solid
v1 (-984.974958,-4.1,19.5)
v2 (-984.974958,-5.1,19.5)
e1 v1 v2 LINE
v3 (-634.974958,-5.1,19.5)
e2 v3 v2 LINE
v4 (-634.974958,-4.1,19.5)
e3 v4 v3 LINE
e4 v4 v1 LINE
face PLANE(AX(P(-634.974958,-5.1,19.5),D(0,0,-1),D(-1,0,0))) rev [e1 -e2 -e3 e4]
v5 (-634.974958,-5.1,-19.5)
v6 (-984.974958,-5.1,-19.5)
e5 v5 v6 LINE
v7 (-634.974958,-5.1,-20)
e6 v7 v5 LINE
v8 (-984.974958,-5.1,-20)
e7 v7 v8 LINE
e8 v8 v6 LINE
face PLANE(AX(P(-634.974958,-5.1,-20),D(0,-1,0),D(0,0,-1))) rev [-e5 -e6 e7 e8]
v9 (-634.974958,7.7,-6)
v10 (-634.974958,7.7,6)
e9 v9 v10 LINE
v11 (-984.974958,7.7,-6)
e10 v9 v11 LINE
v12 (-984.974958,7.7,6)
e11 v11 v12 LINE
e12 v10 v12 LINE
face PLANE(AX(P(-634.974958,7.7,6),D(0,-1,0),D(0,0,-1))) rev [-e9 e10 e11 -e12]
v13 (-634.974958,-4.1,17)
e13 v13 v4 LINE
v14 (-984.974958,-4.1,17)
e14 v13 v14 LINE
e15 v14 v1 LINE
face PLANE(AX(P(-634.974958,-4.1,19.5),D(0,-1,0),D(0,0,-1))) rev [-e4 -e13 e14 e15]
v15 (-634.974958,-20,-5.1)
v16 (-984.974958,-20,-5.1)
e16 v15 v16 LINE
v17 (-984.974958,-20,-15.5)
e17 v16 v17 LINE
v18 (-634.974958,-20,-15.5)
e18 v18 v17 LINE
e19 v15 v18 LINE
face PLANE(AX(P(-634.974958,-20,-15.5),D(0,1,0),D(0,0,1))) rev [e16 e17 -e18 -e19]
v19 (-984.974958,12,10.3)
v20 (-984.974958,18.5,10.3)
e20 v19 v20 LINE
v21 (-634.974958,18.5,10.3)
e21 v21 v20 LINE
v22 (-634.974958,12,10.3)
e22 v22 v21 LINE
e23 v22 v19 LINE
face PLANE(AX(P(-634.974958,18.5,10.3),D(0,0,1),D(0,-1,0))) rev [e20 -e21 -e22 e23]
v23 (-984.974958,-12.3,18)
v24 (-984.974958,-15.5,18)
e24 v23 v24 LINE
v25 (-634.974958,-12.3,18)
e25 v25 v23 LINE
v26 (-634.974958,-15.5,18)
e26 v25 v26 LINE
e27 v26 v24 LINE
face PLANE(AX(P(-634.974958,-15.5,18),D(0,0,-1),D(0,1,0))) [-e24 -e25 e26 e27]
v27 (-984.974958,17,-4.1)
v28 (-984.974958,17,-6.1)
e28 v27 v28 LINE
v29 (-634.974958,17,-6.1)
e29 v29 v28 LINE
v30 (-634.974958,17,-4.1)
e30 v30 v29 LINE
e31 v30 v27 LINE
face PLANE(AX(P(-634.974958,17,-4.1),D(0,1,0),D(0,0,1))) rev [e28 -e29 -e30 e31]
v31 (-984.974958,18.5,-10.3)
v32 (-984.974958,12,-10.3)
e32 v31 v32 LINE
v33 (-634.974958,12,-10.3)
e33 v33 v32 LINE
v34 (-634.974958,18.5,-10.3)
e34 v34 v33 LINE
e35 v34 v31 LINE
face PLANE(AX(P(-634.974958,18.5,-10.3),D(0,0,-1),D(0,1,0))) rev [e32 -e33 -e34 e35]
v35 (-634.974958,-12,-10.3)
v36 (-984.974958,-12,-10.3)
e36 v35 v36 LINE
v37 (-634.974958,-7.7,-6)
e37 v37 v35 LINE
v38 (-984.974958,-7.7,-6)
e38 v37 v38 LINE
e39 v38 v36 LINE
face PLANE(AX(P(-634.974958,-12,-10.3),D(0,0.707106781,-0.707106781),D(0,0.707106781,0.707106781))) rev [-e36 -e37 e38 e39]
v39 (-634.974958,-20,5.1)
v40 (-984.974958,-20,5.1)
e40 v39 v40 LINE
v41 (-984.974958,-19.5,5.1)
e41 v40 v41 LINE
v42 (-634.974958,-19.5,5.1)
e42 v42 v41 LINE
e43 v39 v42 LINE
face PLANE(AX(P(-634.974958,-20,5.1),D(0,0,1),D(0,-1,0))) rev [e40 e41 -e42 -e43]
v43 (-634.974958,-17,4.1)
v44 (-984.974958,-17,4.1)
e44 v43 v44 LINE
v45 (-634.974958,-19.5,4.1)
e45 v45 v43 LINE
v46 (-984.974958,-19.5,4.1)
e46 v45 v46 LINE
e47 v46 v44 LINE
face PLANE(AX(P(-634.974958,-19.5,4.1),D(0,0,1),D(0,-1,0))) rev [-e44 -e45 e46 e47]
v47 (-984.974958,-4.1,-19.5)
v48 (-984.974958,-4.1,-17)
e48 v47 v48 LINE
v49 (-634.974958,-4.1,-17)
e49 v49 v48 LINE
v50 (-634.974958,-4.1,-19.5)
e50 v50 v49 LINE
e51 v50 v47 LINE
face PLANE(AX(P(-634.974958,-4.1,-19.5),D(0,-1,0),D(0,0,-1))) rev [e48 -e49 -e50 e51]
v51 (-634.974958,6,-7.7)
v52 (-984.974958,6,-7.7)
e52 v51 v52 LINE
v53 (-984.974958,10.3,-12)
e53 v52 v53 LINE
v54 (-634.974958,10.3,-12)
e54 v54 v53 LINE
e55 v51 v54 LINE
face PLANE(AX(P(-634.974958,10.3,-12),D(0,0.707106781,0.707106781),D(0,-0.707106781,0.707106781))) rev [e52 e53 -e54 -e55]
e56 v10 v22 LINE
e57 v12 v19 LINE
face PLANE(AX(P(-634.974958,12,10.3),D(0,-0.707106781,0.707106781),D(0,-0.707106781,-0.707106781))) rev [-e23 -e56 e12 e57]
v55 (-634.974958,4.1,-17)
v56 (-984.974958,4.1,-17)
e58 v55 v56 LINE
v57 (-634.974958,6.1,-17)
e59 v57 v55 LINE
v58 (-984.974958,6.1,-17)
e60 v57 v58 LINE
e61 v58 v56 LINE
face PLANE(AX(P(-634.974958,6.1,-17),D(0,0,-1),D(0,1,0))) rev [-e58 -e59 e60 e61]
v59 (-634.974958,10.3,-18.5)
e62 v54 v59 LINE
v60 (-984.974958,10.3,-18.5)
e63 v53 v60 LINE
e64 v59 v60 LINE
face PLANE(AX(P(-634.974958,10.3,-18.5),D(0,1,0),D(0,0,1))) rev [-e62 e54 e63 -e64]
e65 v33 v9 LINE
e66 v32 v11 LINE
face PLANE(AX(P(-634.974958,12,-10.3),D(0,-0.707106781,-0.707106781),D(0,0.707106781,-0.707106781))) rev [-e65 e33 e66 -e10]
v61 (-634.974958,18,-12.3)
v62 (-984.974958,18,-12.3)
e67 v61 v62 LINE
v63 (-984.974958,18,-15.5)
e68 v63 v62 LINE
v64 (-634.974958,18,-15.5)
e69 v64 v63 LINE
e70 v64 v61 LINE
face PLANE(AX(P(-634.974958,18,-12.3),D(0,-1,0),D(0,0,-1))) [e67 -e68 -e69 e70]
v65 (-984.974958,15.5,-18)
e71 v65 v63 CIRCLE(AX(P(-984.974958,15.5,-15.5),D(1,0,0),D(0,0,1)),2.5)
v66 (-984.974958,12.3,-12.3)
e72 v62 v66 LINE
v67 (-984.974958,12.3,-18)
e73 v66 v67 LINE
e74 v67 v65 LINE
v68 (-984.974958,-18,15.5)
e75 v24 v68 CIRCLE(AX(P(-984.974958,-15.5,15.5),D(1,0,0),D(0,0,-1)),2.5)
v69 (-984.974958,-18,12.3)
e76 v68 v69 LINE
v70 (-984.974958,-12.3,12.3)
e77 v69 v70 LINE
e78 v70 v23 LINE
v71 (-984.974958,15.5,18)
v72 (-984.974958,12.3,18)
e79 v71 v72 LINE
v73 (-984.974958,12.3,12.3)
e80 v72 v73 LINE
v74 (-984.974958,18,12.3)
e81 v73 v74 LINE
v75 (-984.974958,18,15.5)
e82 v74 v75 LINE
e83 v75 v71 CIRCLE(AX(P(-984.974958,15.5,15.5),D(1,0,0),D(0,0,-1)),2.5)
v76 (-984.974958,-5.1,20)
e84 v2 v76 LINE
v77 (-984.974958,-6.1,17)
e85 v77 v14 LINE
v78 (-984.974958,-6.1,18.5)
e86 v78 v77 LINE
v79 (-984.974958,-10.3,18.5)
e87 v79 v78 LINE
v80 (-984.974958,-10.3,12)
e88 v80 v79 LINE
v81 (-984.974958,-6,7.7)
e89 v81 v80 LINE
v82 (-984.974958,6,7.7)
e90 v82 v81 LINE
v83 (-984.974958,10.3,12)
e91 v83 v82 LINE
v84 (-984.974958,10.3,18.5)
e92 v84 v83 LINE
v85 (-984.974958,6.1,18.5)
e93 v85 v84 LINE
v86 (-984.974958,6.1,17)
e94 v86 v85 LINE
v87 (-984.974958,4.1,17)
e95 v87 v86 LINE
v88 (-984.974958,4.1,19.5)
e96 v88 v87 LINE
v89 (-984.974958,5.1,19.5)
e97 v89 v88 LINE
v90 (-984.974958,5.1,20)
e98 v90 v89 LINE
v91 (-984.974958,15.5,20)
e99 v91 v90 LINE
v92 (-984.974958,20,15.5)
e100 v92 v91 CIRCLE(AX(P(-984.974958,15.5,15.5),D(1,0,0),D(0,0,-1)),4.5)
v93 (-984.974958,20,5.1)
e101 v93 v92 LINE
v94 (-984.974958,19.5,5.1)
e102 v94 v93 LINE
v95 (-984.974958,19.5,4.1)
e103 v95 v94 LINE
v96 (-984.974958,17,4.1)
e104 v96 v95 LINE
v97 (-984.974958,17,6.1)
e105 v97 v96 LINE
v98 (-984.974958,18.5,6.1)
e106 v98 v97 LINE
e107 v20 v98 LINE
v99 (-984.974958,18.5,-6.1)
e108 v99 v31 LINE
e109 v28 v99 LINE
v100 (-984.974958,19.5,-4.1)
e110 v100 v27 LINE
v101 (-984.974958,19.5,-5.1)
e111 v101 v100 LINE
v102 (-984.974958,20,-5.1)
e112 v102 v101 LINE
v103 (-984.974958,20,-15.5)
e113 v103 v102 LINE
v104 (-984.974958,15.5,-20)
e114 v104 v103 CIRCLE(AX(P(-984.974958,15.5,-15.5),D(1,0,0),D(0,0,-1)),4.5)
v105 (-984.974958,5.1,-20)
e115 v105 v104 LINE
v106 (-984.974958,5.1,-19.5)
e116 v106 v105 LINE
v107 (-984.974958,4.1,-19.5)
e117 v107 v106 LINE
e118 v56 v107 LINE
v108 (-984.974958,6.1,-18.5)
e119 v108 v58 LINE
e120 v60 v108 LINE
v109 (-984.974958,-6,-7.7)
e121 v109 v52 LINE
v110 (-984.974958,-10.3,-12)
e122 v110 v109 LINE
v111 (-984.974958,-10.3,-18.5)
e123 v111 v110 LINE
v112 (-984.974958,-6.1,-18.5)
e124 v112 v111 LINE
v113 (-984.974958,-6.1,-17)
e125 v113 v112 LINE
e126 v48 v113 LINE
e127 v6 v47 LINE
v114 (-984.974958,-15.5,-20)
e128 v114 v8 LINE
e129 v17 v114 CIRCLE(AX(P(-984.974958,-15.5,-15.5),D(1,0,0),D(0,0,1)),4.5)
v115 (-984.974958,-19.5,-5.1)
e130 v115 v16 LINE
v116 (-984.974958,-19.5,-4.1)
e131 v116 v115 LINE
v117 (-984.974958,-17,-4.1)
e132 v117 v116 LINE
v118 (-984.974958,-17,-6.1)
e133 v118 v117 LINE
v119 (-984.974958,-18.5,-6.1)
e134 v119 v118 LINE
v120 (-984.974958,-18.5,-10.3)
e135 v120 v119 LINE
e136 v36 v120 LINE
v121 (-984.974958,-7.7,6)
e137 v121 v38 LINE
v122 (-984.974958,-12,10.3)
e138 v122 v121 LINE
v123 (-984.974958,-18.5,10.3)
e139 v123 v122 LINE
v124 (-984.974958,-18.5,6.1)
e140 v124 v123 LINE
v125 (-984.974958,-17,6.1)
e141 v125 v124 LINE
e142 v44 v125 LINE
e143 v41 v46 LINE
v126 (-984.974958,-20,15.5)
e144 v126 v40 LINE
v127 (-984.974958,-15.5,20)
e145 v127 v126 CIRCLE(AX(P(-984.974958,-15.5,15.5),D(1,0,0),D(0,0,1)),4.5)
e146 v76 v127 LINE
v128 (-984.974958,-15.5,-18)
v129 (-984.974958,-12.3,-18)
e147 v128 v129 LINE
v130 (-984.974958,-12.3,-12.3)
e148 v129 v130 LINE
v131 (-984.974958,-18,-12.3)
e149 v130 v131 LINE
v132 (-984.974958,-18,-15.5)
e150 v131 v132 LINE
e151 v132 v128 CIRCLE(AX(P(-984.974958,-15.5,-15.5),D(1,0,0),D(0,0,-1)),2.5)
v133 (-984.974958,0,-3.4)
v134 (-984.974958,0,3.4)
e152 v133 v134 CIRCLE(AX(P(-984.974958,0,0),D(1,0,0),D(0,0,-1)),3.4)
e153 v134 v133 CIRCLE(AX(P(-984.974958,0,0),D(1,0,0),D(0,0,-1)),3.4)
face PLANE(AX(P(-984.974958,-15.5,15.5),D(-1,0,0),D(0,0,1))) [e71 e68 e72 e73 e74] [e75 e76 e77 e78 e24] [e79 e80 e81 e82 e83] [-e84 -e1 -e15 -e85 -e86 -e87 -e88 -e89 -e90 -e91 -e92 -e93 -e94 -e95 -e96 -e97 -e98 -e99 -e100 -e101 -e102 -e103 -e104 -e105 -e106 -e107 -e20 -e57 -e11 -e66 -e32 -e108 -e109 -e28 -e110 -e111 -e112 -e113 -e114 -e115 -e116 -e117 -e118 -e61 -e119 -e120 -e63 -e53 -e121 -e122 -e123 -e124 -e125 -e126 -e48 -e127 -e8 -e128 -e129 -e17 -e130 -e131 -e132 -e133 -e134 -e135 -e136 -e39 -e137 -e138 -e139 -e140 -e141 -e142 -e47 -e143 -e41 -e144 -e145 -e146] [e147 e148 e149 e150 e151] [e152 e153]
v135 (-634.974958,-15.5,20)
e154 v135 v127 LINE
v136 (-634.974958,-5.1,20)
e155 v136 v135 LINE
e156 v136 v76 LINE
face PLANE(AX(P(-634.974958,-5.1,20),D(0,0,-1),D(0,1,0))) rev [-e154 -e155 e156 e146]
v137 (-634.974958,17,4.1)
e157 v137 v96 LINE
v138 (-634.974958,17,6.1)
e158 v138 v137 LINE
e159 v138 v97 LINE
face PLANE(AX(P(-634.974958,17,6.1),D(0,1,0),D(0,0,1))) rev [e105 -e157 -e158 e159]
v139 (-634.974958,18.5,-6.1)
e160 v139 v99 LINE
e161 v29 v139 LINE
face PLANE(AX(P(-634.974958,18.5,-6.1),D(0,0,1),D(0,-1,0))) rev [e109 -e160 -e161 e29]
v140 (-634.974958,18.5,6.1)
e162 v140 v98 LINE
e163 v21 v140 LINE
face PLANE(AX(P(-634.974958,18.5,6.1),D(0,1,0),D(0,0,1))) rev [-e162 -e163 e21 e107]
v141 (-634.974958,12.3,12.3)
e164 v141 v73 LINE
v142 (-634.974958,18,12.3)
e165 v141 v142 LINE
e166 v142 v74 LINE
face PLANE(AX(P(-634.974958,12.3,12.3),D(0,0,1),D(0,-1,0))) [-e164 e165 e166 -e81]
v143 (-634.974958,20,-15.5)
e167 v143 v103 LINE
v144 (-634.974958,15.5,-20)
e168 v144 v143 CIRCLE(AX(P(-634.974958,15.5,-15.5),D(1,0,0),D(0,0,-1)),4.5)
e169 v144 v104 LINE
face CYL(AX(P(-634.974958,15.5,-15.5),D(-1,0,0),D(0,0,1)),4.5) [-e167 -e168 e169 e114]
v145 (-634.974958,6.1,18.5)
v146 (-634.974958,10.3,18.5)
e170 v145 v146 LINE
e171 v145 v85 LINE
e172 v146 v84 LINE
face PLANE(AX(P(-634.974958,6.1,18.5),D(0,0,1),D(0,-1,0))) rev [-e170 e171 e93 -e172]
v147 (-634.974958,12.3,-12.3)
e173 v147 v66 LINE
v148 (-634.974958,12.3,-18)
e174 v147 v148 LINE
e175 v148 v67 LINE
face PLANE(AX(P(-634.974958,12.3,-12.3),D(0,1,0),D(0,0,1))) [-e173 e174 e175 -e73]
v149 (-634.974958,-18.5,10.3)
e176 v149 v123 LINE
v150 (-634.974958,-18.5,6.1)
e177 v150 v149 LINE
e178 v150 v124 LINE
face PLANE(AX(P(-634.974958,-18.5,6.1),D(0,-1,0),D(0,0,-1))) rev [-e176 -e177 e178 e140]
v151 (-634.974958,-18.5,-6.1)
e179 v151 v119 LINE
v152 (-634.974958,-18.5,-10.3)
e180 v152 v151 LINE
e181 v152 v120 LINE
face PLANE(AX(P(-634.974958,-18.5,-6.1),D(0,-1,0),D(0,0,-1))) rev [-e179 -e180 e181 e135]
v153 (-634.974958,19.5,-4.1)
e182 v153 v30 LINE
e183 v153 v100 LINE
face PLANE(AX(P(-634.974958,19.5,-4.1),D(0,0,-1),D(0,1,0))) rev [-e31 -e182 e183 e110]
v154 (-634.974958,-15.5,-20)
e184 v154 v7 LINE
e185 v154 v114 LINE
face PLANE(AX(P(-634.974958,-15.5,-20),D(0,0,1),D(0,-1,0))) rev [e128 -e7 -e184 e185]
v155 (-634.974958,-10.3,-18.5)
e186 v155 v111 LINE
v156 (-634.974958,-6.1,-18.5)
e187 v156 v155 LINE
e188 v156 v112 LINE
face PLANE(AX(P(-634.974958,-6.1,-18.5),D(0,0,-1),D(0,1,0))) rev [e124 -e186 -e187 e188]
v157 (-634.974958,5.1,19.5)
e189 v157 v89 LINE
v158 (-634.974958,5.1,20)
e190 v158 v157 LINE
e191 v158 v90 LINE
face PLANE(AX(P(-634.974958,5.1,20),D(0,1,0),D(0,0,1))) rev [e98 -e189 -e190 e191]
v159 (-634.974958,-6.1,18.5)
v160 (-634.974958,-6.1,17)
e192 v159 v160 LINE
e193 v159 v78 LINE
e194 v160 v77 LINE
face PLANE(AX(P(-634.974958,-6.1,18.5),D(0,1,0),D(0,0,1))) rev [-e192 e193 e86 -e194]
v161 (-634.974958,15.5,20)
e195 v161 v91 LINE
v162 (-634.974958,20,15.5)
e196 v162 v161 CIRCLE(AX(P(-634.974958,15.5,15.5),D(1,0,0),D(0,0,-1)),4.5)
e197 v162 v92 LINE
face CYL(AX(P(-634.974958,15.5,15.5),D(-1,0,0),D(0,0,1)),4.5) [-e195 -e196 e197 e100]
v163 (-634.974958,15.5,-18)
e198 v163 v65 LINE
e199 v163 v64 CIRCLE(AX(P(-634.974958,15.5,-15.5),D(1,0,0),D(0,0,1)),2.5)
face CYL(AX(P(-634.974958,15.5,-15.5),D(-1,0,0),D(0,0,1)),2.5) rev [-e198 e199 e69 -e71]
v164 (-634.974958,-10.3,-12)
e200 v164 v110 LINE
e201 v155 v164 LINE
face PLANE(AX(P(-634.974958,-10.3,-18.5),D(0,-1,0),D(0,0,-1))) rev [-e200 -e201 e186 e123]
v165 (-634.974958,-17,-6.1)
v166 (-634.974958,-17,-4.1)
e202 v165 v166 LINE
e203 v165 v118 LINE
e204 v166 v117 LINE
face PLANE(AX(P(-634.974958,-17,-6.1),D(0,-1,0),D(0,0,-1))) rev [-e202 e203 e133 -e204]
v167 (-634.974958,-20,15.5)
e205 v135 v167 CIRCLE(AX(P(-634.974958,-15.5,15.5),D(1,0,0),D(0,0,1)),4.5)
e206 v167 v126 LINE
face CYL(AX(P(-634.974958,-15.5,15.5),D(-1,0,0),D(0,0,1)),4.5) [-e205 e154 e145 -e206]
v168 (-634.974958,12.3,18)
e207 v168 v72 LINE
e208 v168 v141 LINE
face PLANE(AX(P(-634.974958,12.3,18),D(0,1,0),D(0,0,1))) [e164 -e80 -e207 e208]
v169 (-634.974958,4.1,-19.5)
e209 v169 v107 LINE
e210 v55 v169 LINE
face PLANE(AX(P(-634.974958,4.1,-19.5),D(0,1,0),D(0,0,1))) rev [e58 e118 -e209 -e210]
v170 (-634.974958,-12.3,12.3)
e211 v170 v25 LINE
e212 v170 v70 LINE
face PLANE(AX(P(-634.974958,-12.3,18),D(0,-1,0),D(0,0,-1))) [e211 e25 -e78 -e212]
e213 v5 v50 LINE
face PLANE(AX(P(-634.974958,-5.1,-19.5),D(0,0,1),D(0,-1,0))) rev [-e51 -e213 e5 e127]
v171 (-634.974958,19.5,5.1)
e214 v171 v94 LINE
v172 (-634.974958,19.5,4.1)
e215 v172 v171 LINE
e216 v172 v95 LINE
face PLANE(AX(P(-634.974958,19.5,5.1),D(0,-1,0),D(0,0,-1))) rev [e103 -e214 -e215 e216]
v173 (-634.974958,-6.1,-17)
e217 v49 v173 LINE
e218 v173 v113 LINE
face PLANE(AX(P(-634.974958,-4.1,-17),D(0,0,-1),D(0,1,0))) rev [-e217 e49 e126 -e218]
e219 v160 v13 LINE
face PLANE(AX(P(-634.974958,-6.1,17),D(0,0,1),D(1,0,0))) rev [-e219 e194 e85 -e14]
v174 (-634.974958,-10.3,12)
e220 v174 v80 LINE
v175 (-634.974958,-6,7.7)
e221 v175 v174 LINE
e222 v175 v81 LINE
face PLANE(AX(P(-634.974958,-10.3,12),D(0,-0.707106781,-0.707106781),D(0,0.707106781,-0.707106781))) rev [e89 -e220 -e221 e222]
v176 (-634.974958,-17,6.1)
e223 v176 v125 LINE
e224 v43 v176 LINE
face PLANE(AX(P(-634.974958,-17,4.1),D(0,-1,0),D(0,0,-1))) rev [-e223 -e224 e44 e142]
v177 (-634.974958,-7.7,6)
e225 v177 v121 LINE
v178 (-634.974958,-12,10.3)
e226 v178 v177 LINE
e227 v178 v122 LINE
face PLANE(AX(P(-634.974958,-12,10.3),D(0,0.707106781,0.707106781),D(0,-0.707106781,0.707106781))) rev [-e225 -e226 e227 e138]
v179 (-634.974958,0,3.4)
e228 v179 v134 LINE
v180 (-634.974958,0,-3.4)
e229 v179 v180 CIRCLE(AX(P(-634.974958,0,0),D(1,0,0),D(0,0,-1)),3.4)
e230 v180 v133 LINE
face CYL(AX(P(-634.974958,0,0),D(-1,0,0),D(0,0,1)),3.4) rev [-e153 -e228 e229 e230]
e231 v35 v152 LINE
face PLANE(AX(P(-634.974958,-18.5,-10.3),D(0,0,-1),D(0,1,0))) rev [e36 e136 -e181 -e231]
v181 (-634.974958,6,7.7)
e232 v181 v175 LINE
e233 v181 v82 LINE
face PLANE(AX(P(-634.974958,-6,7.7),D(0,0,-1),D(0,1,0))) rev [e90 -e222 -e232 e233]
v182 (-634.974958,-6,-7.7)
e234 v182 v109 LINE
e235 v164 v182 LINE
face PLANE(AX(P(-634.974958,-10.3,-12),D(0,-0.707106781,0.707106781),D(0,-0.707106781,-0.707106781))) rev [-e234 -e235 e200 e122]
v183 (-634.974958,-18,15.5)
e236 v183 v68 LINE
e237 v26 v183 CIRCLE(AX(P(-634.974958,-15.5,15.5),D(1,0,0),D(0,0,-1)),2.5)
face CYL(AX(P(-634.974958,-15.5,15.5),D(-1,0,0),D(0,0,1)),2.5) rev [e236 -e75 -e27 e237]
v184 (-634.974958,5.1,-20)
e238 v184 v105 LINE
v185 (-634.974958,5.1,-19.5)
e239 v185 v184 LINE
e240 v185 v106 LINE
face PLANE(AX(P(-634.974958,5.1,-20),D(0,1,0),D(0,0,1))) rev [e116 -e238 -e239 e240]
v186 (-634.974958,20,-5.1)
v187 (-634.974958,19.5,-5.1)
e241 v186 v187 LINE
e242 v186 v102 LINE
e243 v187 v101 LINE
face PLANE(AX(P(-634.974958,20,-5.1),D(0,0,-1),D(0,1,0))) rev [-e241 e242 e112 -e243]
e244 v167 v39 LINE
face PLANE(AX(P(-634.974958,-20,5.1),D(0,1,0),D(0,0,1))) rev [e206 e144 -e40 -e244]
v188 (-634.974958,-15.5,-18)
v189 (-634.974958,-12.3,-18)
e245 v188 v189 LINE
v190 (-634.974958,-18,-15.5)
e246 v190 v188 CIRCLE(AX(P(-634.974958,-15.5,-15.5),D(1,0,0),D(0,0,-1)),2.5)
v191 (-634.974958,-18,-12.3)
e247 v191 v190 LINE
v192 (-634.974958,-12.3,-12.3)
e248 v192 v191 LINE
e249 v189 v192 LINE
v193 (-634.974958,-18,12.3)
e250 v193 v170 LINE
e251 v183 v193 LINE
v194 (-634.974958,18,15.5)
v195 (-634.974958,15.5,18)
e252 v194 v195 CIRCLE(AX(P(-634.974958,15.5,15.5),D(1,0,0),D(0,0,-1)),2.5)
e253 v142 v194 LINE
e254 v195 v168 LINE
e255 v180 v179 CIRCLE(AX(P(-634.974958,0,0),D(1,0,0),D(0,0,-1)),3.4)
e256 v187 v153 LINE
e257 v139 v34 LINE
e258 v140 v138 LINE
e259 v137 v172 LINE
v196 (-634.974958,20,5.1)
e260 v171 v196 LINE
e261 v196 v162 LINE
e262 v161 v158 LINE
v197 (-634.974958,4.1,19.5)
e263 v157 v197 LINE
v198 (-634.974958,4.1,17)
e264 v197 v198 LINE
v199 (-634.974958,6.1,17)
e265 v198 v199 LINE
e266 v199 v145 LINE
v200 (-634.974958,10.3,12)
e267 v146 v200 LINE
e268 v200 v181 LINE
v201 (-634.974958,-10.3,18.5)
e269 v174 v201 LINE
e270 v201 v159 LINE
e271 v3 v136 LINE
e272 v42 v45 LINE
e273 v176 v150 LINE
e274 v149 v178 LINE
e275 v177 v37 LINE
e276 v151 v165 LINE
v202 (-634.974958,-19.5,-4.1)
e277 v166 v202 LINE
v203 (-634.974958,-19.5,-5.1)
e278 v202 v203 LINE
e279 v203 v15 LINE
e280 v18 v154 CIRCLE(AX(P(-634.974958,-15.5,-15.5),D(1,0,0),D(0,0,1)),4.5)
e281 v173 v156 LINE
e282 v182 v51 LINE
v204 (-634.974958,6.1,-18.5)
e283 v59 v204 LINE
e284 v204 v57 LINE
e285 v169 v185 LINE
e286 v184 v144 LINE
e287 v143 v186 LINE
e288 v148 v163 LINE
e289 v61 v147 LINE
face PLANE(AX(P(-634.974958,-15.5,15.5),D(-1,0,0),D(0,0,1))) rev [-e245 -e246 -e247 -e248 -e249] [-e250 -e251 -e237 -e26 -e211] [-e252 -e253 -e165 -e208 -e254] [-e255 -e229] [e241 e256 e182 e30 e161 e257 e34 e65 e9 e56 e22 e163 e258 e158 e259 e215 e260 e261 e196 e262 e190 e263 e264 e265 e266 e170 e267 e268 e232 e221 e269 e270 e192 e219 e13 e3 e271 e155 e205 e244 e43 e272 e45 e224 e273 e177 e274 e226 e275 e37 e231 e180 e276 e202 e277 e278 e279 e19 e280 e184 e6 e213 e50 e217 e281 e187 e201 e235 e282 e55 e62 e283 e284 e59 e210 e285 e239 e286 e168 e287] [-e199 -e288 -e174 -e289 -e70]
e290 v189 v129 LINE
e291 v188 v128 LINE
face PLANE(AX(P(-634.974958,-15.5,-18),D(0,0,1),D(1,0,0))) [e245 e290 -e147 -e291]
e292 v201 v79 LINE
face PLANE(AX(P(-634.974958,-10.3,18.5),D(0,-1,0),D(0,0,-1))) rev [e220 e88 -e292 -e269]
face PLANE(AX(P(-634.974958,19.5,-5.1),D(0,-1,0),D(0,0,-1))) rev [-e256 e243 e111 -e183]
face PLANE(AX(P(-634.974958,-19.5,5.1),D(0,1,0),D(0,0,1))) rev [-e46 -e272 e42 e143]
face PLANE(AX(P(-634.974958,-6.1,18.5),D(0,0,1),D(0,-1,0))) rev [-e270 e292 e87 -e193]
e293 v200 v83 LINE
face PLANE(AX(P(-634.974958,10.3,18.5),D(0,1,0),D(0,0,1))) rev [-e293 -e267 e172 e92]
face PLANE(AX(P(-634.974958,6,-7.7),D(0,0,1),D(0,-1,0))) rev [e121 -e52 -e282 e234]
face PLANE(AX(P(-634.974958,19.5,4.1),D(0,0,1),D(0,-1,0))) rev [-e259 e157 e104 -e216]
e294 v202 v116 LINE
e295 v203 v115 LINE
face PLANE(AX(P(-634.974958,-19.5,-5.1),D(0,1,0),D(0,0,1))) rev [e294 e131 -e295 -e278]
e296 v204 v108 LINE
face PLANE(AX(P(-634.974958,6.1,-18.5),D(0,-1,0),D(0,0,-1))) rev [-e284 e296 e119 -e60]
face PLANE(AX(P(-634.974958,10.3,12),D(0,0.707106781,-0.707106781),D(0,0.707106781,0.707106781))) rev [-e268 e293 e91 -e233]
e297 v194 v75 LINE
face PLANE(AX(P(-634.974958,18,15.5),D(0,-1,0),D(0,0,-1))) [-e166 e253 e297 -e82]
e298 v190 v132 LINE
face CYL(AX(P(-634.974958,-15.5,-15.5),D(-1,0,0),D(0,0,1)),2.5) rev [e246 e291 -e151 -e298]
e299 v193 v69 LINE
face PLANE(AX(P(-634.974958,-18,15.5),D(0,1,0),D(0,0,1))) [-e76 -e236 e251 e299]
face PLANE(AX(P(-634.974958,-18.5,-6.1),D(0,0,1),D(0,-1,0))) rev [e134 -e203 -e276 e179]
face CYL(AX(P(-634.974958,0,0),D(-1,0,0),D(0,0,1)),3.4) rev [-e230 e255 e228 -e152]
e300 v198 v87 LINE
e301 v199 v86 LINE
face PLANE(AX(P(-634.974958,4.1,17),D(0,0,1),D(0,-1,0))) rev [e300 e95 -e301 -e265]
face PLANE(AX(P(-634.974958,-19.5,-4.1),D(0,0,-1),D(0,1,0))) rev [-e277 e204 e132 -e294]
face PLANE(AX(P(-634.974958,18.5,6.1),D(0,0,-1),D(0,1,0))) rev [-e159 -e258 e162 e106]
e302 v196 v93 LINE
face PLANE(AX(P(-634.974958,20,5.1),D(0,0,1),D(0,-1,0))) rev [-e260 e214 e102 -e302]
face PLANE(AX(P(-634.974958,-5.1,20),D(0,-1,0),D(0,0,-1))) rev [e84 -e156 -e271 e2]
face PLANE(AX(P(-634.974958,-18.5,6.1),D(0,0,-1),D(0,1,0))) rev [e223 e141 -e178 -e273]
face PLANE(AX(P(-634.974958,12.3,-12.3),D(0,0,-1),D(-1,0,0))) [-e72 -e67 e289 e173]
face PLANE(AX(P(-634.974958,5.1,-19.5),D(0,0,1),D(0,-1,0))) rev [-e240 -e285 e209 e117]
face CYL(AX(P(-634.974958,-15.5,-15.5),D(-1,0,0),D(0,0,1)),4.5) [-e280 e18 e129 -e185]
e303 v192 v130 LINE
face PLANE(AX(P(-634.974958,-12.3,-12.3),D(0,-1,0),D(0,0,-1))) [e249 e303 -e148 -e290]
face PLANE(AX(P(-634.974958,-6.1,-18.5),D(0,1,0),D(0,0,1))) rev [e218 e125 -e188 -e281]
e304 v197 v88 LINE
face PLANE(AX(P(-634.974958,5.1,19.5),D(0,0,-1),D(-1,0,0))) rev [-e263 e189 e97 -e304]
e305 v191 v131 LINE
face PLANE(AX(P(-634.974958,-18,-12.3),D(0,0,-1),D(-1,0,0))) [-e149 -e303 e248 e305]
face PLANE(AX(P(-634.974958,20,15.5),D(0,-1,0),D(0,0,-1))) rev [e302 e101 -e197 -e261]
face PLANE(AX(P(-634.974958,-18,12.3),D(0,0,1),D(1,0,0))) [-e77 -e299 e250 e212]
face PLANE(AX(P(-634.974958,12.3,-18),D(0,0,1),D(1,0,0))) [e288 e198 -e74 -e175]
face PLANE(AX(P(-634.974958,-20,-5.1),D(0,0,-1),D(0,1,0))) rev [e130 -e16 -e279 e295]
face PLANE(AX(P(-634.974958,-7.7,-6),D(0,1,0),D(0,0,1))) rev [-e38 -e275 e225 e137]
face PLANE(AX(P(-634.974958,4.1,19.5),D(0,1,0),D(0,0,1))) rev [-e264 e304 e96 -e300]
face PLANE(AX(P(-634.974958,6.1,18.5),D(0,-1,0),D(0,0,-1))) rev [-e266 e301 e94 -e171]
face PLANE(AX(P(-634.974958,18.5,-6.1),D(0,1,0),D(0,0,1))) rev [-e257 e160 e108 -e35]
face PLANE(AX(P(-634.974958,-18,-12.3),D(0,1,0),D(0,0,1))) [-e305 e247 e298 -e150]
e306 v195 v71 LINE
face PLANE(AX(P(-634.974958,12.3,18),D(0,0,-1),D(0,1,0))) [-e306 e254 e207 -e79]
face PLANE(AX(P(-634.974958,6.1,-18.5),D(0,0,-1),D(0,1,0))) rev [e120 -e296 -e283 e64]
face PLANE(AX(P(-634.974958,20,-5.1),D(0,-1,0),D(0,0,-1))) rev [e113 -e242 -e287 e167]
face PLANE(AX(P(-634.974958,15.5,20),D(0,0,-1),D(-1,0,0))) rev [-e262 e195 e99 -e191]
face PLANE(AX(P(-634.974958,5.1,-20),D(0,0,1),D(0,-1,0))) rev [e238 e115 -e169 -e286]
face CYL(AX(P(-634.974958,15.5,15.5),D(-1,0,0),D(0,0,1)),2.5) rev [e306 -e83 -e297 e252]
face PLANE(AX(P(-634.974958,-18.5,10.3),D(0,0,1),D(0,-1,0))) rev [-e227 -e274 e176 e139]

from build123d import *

# Parameters (mm, degrees)
SKETCH1_R                                 = 3.4
ALUMINIUM_PROFILE_40_X_40B_X_R4_5_1_DEPTH = 350


with BuildPart() as part:
    # Sketch1 → Aluminium profile 40 X 40B X R4.5(1) (new body)
    with BuildSketch(Plane.YZ.offset(-984.974958264)):
        with BuildLine():
            Line((-5.1, 20), (-5.1, 19.5))
            Line((-5.1, 19.5), (-4.1, 19.5))
            Line((-4.1, 19.5), (-4.1, 17))
            Line((-4.1, 17), (-6.1, 17))
            Line((-6.1, 17), (-6.1, 18.5))
            Line((-6.1, 18.5), (-10.3, 18.5))
            Line((-10.3, 18.5), (-10.3, 12))
            Line((-10.3, 12), (-6, 7.7))
            Line((-6, 7.7), (6, 7.7))
            Line((6, 7.7), (10.3, 12))
            Line((10.3, 12), (10.3, 18.5))
            Line((10.3, 18.5), (6.1, 18.5))
            Line((6.1, 18.5), (6.1, 17))
            Line((6.1, 17), (4.1, 17))
            Line((4.1, 17), (4.1, 19.5))
            Line((4.1, 19.5), (5.1, 19.5))
            Line((5.1, 19.5), (5.1, 20))
            Line((5.1, 20), (15.5, 20))
            ThreePointArc((15.5, 20), (18.681980515, 18.681980515), (20, 15.5))
            Line((20, 15.5), (20, 5.1))
            Line((20, 5.1), (19.5, 5.1))
            Line((19.5, 5.1), (19.5, 4.1))
            Line((19.5, 4.1), (17, 4.1))
            Line((17, 4.1), (17, 6.1))
            Line((17, 6.1), (18.5, 6.1))
            Line((18.5, 6.1), (18.5, 10.3))
            Line((18.5, 10.3), (12, 10.3))
            Line((12, 10.3), (7.7, 6))
            Line((7.7, 6), (7.7, -6))
            Line((7.7, -6), (12, -10.3))
            Line((12, -10.3), (18.5, -10.3))
            Line((18.5, -10.3), (18.5, -6.1))
            Line((18.5, -6.1), (17, -6.1))
            Line((17, -6.1), (17, -4.1))
            Line((17, -4.1), (19.5, -4.1))
            Line((19.5, -4.1), (19.5, -5.1))
            Line((19.5, -5.1), (20, -5.1))
            Line((20, -5.1), (20, -15.5))
            ThreePointArc((20, -15.5), (18.681980515, -18.681980515), (15.5, -20))
            Line((15.5, -20), (5.1, -20))
            Line((5.1, -20), (5.1, -19.5))
            Line((5.1, -19.5), (4.1, -19.5))
            Line((4.1, -19.5), (4.1, -17))
            Line((4.1, -17), (6.1, -17))
            Line((6.1, -17), (6.1, -18.5))
            Line((6.1, -18.5), (10.3, -18.5))
            Line((10.3, -18.5), (10.3, -12))
            Line((10.3, -12), (6, -7.7))
            Line((6, -7.7), (-6, -7.7))
            Line((-6, -7.7), (-10.3, -12))
            Line((-10.3, -12), (-10.3, -18.5))
            Line((-10.3, -18.5), (-6.1, -18.5))
            Line((-6.1, -18.5), (-6.1, -17))
            Line((-6.1, -17), (-4.1, -17))
            Line((-4.1, -17), (-4.1, -19.5))
            Line((-4.1, -19.5), (-5.1, -19.5))
            Line((-5.1, -19.5), (-5.1, -20))
            Line((-5.1, -20), (-15.5, -20))
            ThreePointArc((-15.5, -20), (-18.681980515, -18.681980515), (-20, -15.5))
            Line((-20, -15.5), (-20, -5.1))
            Line((-20, -5.1), (-19.5, -5.1))
            Line((-19.5, -5.1), (-19.5, -4.1))
            Line((-19.5, -4.1), (-17, -4.1))
            Line((-17, -4.1), (-17, -6.1))
            Line((-17, -6.1), (-18.5, -6.1))
            Line((-18.5, -6.1), (-18.5, -10.3))
            Line((-18.5, -10.3), (-12, -10.3))
            Line((-12, -10.3), (-7.7, -6))
            Line((-7.7, -6), (-7.7, 6))
            Line((-7.7, 6), (-12, 10.3))
            Line((-12, 10.3), (-18.5, 10.3))
            Line((-18.5, 10.3), (-18.5, 6.1))
            Line((-18.5, 6.1), (-17, 6.1))
            Line((-17, 6.1), (-17, 4.1))
            Line((-17, 4.1), (-19.5, 4.1))
            Line((-19.5, 4.1), (-19.5, 5.1))
            Line((-19.5, 5.1), (-20, 5.1))
            Line((-20, 5.1), (-20, 15.5))
            ThreePointArc((-20, 15.5), (-18.681980515, 18.681980515), (-15.5, 20))
            Line((-15.5, 20), (-5.1, 20))
        make_face()
        Circle(SKETCH1_R, mode=Mode.SUBTRACT)
        with BuildLine():
            Line((12.3, 18), (15.5, 18))
            ThreePointArc((15.5, 18), (17.267766953, 17.267766953), (18, 15.5))
            Line((18, 15.5), (18, 12.3))
            Line((18, 12.3), (12.3, 12.3))
            Line((12.3, 12.3), (12.3, 18))
        make_face(mode=Mode.SUBTRACT)
        with BuildLine():
            Line((-15.5, 18), (-12.3, 18))
            Line((-12.3, 18), (-12.3, 12.3))
            Line((-12.3, 12.3), (-18, 12.3))
            Line((-18, 12.3), (-18, 15.5))
            ThreePointArc((-18, 15.5), (-17.267766953, 17.267766953), (-15.5, 18))
        make_face(mode=Mode.SUBTRACT)
        with BuildLine():
            Line((-18, -12.3), (-12.3, -12.3))
            Line((-12.3, -12.3), (-12.3, -18))
            Line((-12.3, -18), (-15.5, -18))
            ThreePointArc((-15.5, -18), (-17.267766953, -17.267766953), (-18, -15.5))
            Line((-18, -15.5), (-18, -12.3))
        make_face(mode=Mode.SUBTRACT)
        with BuildLine():
            Line((12.3, -12.3), (18, -12.3))
            Line((18, -12.3), (18, -15.5))
            ThreePointArc((18, -15.5), (17.267766953, -17.267766953), (15.5, -18))
            Line((15.5, -18), (12.3, -18))
            Line((12.3, -18), (12.3, -12.3))
        make_face(mode=Mode.SUBTRACT)
    extrude(amount=ALUMINIUM_PROFILE_40_X_40B_X_R4_5_1_DEPTH)


solid = part.part
